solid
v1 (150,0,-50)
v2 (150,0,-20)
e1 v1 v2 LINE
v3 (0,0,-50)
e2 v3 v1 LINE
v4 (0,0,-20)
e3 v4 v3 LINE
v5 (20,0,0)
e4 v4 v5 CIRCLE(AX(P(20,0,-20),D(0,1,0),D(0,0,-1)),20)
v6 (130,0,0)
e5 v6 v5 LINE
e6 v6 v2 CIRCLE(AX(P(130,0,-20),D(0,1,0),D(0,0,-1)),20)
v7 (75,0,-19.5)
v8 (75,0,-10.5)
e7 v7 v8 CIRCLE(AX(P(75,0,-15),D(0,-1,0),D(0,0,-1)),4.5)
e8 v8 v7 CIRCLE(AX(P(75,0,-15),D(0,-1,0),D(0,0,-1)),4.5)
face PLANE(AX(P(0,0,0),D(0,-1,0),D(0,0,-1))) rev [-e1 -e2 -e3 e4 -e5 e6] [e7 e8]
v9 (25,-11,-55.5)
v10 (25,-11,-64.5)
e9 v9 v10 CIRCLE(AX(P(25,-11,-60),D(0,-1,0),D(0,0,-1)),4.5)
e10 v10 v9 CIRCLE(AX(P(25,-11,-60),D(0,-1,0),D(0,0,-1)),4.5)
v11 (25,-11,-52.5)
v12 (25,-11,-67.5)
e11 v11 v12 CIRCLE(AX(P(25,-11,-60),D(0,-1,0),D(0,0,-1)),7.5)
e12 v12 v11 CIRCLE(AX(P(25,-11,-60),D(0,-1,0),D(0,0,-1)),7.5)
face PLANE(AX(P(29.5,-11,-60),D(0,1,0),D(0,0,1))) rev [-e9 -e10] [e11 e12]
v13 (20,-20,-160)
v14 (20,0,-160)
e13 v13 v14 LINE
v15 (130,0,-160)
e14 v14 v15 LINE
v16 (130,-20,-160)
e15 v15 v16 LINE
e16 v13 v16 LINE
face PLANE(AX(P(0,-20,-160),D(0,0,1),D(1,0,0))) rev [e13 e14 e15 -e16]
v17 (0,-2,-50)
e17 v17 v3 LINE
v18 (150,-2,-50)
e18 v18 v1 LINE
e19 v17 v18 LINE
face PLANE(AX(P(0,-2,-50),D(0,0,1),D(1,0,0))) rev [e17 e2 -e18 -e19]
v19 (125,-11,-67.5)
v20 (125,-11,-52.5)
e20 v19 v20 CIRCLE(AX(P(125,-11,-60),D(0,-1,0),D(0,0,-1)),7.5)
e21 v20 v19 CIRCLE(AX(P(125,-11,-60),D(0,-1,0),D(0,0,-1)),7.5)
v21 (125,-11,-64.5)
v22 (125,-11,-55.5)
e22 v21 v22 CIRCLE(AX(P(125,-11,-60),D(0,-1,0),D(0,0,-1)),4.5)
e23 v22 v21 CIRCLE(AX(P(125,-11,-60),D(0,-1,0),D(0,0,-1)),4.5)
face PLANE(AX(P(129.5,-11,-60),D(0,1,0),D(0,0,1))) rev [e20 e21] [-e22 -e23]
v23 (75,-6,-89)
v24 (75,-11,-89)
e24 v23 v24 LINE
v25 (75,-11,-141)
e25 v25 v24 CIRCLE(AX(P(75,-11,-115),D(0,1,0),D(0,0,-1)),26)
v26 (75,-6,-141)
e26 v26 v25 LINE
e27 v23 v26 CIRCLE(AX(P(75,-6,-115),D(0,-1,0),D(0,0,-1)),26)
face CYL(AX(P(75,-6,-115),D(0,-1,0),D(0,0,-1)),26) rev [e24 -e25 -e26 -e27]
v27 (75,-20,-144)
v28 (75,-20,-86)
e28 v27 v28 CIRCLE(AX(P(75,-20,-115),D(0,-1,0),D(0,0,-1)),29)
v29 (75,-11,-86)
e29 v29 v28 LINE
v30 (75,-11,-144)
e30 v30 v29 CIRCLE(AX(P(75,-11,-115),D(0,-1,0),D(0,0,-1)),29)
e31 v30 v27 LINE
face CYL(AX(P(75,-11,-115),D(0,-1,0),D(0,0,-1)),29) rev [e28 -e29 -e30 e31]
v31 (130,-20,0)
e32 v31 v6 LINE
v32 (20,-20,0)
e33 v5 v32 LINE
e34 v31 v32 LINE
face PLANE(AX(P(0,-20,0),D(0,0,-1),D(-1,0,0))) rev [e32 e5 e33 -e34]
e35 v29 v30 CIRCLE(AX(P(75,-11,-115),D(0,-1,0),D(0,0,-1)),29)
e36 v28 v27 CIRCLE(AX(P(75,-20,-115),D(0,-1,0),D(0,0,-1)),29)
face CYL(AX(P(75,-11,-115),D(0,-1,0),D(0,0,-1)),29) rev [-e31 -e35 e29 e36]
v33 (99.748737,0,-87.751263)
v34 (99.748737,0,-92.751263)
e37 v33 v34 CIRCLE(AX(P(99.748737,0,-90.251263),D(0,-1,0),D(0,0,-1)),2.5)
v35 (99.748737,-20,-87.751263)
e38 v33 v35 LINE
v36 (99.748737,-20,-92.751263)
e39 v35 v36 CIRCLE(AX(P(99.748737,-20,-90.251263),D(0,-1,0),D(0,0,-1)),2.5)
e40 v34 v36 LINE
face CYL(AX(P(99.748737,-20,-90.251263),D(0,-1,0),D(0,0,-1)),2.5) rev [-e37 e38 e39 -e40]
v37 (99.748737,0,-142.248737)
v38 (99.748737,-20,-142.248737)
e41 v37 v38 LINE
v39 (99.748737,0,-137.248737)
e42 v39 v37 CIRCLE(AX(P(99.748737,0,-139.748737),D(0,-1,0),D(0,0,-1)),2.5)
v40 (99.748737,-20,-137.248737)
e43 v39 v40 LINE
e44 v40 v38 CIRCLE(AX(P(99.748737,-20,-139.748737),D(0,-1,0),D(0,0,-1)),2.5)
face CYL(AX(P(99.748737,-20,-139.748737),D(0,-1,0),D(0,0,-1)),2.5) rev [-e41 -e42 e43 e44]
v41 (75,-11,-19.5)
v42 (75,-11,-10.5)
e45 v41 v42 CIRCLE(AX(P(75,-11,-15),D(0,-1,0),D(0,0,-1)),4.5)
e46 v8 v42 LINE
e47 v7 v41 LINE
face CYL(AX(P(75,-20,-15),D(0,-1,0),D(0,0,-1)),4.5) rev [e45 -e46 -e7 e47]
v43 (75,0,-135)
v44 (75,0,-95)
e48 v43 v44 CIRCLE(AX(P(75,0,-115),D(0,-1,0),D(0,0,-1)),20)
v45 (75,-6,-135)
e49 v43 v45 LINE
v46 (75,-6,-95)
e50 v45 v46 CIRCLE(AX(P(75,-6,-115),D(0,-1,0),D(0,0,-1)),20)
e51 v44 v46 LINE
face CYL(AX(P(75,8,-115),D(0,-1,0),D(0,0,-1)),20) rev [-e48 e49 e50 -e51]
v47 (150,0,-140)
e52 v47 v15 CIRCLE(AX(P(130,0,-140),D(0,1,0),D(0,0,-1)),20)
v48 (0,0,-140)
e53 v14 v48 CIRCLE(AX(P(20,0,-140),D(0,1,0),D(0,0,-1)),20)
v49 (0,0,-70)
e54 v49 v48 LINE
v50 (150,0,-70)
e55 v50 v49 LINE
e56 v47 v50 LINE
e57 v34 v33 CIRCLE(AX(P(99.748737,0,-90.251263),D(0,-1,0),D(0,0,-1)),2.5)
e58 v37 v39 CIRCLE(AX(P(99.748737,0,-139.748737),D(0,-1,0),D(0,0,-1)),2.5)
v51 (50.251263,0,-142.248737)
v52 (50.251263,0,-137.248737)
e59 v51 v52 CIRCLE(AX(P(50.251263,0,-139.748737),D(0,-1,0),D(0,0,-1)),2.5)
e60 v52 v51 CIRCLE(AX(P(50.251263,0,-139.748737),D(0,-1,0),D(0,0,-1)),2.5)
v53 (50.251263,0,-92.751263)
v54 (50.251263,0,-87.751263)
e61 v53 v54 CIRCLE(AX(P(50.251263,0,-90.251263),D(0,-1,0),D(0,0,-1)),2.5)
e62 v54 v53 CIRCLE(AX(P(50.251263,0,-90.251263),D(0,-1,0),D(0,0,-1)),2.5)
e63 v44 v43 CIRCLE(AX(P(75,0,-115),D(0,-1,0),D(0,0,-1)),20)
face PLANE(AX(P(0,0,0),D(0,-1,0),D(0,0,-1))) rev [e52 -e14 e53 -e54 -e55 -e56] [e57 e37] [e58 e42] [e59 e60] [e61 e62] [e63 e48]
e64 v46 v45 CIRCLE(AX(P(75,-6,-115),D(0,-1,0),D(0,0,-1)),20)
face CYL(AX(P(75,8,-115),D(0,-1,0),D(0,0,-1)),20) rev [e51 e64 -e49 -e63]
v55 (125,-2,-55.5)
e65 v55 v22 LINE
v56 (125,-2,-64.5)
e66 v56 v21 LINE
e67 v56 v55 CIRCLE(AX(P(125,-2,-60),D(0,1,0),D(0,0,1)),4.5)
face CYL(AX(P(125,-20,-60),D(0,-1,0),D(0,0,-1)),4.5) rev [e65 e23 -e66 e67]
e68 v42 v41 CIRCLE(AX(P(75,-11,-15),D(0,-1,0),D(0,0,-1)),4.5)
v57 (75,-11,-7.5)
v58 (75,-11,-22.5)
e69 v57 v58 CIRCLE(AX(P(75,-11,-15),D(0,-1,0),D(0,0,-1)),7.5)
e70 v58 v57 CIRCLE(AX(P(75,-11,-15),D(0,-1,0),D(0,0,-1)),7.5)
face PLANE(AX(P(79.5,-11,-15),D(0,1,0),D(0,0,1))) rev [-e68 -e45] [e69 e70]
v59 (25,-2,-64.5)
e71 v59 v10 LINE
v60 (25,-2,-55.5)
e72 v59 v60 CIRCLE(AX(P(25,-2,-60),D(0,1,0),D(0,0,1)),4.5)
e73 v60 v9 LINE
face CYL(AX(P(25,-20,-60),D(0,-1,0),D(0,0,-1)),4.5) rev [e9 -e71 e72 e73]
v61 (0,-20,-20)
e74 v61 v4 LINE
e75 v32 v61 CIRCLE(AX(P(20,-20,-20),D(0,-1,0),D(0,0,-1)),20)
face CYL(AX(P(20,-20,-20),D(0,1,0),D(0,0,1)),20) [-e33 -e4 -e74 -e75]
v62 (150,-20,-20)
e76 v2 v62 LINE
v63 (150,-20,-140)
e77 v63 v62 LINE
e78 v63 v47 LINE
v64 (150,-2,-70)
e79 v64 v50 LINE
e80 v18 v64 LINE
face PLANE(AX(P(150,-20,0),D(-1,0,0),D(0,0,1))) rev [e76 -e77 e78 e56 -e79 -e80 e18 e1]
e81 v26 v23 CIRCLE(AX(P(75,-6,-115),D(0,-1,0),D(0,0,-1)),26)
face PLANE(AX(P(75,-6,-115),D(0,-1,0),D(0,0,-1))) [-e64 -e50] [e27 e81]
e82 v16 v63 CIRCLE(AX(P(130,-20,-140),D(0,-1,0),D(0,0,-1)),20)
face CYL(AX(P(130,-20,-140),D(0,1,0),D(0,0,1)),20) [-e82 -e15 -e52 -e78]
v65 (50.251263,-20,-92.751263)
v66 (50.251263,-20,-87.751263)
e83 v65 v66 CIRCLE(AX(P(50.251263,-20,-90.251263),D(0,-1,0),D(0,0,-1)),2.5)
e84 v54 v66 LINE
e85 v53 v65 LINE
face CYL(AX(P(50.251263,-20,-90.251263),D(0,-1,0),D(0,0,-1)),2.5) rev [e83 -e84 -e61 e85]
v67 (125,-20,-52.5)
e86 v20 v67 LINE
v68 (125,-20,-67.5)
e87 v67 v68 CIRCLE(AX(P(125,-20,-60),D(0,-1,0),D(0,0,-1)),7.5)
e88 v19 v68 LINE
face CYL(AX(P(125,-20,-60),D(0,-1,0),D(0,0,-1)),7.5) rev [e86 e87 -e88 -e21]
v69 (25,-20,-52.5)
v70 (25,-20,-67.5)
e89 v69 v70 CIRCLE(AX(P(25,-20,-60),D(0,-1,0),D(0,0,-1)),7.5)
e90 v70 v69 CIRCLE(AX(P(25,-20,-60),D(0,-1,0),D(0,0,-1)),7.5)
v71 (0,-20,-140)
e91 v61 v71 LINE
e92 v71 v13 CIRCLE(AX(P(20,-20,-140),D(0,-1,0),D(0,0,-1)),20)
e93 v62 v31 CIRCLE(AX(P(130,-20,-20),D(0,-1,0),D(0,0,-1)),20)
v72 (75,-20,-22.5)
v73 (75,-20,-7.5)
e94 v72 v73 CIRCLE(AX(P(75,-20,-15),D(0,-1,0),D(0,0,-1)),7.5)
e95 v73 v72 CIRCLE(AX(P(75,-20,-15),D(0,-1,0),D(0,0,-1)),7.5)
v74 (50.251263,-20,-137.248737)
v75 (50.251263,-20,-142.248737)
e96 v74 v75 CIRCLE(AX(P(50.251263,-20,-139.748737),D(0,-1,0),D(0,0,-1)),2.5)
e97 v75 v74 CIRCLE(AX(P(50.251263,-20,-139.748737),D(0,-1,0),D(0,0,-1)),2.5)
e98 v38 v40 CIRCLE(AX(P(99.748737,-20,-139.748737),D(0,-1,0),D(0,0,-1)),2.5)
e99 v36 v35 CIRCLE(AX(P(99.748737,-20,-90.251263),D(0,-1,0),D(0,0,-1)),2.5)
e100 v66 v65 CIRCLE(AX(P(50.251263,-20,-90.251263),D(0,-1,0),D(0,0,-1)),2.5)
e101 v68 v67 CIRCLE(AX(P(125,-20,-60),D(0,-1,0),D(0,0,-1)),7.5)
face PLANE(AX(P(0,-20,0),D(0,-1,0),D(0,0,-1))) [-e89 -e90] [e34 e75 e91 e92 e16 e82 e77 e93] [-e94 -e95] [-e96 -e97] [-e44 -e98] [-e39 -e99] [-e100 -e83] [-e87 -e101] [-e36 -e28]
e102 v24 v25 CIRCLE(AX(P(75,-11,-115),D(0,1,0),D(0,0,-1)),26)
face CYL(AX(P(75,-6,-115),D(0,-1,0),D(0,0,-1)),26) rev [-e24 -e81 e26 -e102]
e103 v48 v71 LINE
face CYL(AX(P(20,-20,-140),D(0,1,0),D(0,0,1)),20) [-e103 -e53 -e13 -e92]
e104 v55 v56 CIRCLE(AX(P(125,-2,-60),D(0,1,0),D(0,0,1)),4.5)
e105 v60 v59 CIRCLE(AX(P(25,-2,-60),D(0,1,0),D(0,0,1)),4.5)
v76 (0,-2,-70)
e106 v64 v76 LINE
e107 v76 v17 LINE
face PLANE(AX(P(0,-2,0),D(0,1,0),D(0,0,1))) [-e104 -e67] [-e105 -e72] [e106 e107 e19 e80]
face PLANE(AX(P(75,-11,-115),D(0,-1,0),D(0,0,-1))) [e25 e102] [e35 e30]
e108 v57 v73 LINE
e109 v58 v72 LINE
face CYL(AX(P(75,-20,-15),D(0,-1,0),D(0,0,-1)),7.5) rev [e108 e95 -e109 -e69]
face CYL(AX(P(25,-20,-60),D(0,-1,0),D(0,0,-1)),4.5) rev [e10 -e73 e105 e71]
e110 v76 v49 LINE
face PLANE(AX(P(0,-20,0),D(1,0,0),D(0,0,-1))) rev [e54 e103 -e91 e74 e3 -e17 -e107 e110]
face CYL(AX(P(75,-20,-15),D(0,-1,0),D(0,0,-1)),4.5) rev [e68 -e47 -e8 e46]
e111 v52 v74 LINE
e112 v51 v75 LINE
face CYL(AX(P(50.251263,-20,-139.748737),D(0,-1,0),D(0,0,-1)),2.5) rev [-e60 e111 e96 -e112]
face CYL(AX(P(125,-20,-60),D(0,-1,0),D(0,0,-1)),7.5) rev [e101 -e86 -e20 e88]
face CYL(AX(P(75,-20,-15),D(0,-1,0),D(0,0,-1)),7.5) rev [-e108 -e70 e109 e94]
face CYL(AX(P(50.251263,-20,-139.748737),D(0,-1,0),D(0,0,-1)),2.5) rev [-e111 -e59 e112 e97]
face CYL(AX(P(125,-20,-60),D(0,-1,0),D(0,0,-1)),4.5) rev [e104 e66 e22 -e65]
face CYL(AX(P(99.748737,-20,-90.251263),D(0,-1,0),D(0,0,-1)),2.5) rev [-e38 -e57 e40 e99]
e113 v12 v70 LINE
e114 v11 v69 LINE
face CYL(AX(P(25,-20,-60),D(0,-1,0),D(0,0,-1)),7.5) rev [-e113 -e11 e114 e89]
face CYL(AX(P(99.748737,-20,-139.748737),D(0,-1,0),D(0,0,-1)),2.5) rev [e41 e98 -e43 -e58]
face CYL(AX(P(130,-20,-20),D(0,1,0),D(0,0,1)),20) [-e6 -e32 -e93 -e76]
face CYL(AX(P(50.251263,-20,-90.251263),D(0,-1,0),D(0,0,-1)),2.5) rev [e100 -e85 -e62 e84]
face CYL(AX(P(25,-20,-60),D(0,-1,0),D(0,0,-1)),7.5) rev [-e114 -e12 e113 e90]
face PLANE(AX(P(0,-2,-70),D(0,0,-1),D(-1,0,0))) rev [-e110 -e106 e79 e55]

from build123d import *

# Parameters (mm, degrees)
SKETCH1_W                                           = 150
SKETCH1_H                                           = 160
BOSS_EXTRUDE1_DEPTH                                 = 20
SKETCH2_R                                           = 26
CUT_EXTRUDE1_DEPTH                                  = 14
SKETCH3_R                                           = 20
CUT_EXTRUDE2_DEPTH                                  = 14
M6_TAPPED_HOLE1_D                                   = 5
SKETCH9_R                                           = 29
CUT_EXTRUDE4_DEPTH                                  = 9
FILLET1_R                                           = 20
SKETCH10_W                                          = 150
SKETCH10_H                                          = 20
CUT_EXTRUDE5_DEPTH                                  = 2
HOLE_SIZE_BY_SOCKET_HEAD_CAP_SCREW_TYPE_D           = 9
HOLE_SIZE_BY_SOCKET_HEAD_CAP_SCREW_TYPE_CBORE_D     = 15
HOLE_SIZE_BY_SOCKET_HEAD_CAP_SCREW_TYPE_CBORE_DEPTH = 9


with BuildPart() as part:
    # Sketch1 → Boss-Extrude1 (new body)
    with BuildSketch(Plane.XZ):
        with Locations((75, -80)):
            Rectangle(SKETCH1_W, SKETCH1_H)
    extrude(amount=BOSS_EXTRUDE1_DEPTH)

    # Sketch2 → Cut-Extrude1 (cut)
    with BuildSketch(Plane.XZ.offset(20)):
        with Locations(Location((75, -115, 0), (0, 0, 270))):
            Circle(SKETCH2_R)
    extrude(amount=-CUT_EXTRUDE1_DEPTH, mode=Mode.SUBTRACT)

    # Sketch3 → Cut-Extrude2 (cut)
    with BuildSketch(Plane.XZ.offset(6)):
        with Locations(Location((75, -115, 0), (0, 0, 270))):
            Circle(SKETCH3_R)
    extrude(amount=-CUT_EXTRUDE2_DEPTH, mode=Mode.SUBTRACT)

    # M6 Tapped Hole1 (through all)
    with Locations(Plane(origin=(0, -20, 0), x_dir=(-1, 0, 0), z_dir=(0, -1, 0))):
        with Locations((-99.748737342, 139.748737342), (-50.251262658, 139.748737342), (-50.251262658, 90.251262658), (-99.748737342, 90.251262658)):
            Hole(M6_TAPPED_HOLE1_D / 2)

    # Sketch9 → Cut-Extrude4 (cut)
    with BuildSketch(Plane.XZ.offset(20)):
        with Locations(Location((75, -115, 0), (0, 0, 270))):
            Circle(SKETCH9_R)
    extrude(amount=-CUT_EXTRUDE4_DEPTH, mode=Mode.SUBTRACT)

    # Fillet1
    fillet1_edges = [part.edges().sort_by_distance(p)[0] for p in [
        (0, -10, 0),
        (150, -10, 0),
        (150, -10, -160),
        (0, -10, -160),
    ]]
    fillet(fillet1_edges, radius=FILLET1_R)

    # Sketch10 → Cut-Extrude5 (cut)
    with BuildSketch(Plane(origin=(0, 0, 0), x_dir=(1, 0, 0), z_dir=(0, 1, 0))):
        with Locations((75, 60)):
            Rectangle(SKETCH10_W, SKETCH10_H)
    extrude(amount=-CUT_EXTRUDE5_DEPTH, mode=Mode.SUBTRACT)

    # Hole size (by socket head cap screw type)1 (through all)
    with Locations(Plane(origin=(0, -20, 0), x_dir=(-1, 0, 0), z_dir=(0, -1, 0))):
        with Locations((-125, 60), (-25, 60), (-75, 15)):
            CounterBoreHole(HOLE_SIZE_BY_SOCKET_HEAD_CAP_SCREW_TYPE_D / 2, HOLE_SIZE_BY_SOCKET_HEAD_CAP_SCREW_TYPE_CBORE_D / 2, HOLE_SIZE_BY_SOCKET_HEAD_CAP_SCREW_TYPE_CBORE_DEPTH)


solid = part.part
